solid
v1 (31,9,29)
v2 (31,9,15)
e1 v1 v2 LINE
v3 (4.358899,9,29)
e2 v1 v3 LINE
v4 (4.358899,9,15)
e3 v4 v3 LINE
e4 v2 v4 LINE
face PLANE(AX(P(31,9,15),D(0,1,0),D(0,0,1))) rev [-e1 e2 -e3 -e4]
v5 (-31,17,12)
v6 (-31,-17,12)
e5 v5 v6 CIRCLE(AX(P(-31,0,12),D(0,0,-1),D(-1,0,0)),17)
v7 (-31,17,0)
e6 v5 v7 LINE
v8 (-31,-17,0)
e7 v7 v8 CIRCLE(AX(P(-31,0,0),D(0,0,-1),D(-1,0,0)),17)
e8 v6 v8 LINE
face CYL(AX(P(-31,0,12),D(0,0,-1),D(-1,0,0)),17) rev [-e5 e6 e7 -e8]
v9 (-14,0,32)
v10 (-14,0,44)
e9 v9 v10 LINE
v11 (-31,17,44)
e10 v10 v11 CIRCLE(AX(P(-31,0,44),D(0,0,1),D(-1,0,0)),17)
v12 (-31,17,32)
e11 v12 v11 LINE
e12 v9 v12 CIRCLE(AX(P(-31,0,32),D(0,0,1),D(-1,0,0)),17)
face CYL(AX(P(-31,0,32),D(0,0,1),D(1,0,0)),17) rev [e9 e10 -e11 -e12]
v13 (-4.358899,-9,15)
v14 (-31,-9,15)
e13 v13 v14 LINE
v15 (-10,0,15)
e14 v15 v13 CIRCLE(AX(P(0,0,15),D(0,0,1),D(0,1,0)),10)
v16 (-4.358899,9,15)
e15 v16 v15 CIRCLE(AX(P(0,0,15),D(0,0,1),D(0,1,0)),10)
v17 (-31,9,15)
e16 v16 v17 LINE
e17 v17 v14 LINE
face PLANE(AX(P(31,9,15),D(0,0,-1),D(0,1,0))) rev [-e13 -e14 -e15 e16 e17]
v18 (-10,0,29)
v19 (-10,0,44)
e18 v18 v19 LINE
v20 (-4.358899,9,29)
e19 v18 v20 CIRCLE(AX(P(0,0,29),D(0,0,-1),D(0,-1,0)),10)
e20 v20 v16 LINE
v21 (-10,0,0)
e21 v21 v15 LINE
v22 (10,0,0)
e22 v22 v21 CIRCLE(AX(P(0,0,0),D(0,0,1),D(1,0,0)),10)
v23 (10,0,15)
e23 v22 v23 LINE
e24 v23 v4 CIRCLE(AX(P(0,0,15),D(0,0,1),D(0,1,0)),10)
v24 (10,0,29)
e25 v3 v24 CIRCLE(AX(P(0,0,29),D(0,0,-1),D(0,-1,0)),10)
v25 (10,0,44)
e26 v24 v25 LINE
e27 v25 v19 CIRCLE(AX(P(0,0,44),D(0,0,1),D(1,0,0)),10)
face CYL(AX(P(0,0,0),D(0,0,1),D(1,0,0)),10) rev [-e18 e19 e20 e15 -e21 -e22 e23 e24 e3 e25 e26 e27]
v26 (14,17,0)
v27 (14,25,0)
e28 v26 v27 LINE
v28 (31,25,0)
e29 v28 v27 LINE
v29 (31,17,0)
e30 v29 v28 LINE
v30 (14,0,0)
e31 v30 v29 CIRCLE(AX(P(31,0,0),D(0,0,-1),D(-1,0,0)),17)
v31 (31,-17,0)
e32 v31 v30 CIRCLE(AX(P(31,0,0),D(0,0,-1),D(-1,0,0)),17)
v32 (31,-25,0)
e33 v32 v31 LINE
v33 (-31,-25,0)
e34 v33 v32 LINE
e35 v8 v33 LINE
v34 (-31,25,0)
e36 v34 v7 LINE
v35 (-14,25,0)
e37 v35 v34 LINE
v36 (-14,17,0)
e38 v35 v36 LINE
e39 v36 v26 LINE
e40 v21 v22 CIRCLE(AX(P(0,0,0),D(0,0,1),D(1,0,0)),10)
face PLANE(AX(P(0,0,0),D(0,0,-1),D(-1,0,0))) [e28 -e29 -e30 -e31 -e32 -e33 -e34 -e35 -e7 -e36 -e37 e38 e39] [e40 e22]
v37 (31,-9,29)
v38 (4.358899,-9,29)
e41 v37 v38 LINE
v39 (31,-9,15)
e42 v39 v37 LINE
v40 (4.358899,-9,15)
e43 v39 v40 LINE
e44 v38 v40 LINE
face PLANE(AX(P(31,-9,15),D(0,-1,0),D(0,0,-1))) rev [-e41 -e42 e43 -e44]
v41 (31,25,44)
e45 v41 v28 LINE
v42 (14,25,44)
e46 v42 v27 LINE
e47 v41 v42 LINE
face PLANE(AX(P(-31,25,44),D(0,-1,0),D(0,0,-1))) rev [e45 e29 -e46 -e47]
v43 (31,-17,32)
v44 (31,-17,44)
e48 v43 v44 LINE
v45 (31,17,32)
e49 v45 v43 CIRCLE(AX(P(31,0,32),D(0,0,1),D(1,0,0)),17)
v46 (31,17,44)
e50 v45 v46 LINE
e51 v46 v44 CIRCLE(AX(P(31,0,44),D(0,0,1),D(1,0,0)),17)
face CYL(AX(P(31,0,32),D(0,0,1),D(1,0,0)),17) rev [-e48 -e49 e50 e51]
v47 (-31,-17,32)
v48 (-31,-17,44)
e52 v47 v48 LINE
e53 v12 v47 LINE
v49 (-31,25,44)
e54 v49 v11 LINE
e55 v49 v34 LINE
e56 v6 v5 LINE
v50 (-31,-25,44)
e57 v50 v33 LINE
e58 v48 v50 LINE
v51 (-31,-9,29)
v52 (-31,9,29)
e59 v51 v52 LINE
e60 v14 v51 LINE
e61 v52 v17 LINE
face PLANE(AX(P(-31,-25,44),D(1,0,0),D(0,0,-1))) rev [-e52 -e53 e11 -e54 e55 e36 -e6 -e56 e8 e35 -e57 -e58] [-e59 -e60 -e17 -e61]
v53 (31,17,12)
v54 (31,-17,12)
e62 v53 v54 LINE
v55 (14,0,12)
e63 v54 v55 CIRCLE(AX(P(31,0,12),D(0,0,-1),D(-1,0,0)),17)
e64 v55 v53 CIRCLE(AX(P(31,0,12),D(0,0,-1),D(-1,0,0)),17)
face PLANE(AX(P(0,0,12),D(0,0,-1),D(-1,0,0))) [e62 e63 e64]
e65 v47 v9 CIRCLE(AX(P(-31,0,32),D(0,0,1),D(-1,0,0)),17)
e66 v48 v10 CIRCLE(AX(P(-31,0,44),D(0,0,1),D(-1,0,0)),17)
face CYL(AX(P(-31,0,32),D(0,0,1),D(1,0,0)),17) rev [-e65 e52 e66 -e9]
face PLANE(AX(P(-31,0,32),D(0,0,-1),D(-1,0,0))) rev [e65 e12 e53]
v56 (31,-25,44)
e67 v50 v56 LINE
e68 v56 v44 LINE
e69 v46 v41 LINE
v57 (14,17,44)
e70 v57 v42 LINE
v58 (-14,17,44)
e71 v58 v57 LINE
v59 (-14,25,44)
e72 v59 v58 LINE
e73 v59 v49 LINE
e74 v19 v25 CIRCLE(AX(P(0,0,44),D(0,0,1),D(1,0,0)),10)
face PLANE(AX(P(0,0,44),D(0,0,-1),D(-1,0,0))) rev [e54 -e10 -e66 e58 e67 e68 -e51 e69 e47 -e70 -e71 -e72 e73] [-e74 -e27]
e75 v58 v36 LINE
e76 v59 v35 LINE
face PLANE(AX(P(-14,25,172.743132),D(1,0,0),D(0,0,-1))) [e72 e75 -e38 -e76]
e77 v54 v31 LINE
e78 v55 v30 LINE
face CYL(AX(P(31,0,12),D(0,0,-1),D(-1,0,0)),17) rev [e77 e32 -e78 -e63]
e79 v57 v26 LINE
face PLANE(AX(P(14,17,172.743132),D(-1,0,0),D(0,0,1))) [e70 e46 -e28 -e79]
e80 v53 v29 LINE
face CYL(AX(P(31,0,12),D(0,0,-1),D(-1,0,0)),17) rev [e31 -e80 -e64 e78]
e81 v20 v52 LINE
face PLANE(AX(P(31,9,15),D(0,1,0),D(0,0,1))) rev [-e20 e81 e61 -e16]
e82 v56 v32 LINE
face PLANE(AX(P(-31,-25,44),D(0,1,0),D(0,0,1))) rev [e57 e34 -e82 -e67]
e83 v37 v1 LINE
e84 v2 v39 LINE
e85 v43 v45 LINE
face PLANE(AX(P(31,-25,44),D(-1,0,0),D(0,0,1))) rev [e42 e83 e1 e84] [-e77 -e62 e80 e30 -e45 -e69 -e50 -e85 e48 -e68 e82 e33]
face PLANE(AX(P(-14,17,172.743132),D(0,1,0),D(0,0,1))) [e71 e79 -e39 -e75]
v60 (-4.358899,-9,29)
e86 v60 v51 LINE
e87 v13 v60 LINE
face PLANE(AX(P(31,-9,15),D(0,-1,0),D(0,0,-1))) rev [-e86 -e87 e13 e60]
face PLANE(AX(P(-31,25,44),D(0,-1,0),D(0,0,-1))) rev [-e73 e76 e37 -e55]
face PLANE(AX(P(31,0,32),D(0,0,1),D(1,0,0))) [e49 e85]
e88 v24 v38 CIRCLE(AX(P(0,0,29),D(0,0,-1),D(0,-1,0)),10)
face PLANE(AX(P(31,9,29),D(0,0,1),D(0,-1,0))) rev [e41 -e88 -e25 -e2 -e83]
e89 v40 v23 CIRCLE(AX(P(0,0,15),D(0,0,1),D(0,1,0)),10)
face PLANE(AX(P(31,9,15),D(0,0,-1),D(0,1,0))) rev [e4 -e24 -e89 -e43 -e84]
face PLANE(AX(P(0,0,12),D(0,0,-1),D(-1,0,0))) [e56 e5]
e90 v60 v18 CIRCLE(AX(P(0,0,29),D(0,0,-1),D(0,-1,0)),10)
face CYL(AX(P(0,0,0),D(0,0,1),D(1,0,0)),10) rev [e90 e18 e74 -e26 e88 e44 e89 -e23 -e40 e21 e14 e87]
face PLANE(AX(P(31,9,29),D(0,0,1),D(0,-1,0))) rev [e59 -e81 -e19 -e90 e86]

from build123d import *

# Parameters (mm, degrees)
BLOCK_PROFILE_SKETCH_W     = 62
BLOCK_PROFILE_SKETCH_H     = 50
BLOCK_62X50X44_DEPTH       = 44
THROUGH_HOLE_SKETCH_R      = 10
THROUGH_HOLE_20_DEPTH      = 44
TOP_SLOT_34X12_DEPTH       = 12
RELIEF_CUT_A_DEPTH         = 12
SIDE_RELIEF_CUT_DEPTH      = 60.3464405
SIDE_RELIEF_CUT_DEPTH_BACK = 60.3464405
RELIEF_START               = -12
RELIEF_CUT_B_DEPTH         = 12
RELIEF_CUT_C_DEPTH         = 12
WINDOW_SKETCH_W            = 14
WINDOW_SKETCH_H            = 18
WINDOW_CUT_DEPTH           = 81.031243899


with BuildPart() as part:
    # Block Profile Sketch → Block 62x50x44 (new body)
    with BuildSketch(Plane.XY):
        Rectangle(BLOCK_PROFILE_SKETCH_W, BLOCK_PROFILE_SKETCH_H)
    extrude(amount=BLOCK_62X50X44_DEPTH)

    # Through Hole Sketch → Through Hole Ø20 (cut)
    with BuildSketch(Plane.XY.offset(44)):
        Circle(THROUGH_HOLE_SKETCH_R)
    extrude(amount=-THROUGH_HOLE_20_DEPTH, mode=Mode.SUBTRACT)

    # Top Slot Sketch → Top Slot 34x12 (cut)
    with BuildSketch(Plane.XY.offset(44)):
        with BuildLine():
            Line((31, 17), (31, -17))
            ThreePointArc((31, -17), (14, 0), (31, 17))
        make_face()
    extrude(amount=-TOP_SLOT_34X12_DEPTH, mode=Mode.SUBTRACT)

    # Relief Cut A Sketch → Relief Cut A (cut)
    with BuildSketch(Plane.XY.offset(44)):
        with BuildLine():
            Line((31, -17), (31, 17))
            ThreePointArc((31, 17), (14, 0), (31, -17))
        make_face()
        with BuildLine():
            Line((-31, -17), (-31, 17))
            ThreePointArc((-31, 17), (-14, 0), (-31, -17))
        make_face()
    extrude(amount=-RELIEF_CUT_A_DEPTH, mode=Mode.SUBTRACT)

    # Side Relief Sketch → Side Relief Cut (cut, two sides: drawn at the far end of the back side and taken through both)
    with BuildSketch(Plane.XY.offset(44).offset(-SIDE_RELIEF_CUT_DEPTH_BACK)):
        Polygon((-14, 169.536240471), (-14, 25), (-14, 17), (14, 17), (14, 25), (14, 169.536240471), (14, 458.608721412), (-14, 458.608721412), align=None)
    extrude(amount=SIDE_RELIEF_CUT_DEPTH + SIDE_RELIEF_CUT_DEPTH_BACK, mode=Mode.SUBTRACT)

    # Relief Cut B Sketch → Relief Cut B (cut)
    with BuildSketch(Plane(origin=(0, 0, 0), x_dir=(-1, 0, 0), z_dir=(0, 0, -1)).offset(RELIEF_START)):
        with BuildLine():
            ThreePointArc((31, 17), (14, 0), (31, -17))
            Line((31, -17), (31, 17))
        make_face()
    extrude(amount=RELIEF_CUT_B_DEPTH, mode=Mode.SUBTRACT)

    # Relief Cut C Sketch → Relief Cut C (cut)
    with BuildSketch(Plane(origin=(0, 0, 0), x_dir=(-1, 0, 0), z_dir=(0, 0, -1)).offset(RELIEF_START)):
        with BuildLine():
            ThreePointArc((-31, -17), (-14, 0), (-31, 17))
            Line((-31, 17), (-31, -17))
        make_face()
    extrude(amount=RELIEF_CUT_C_DEPTH, mode=Mode.SUBTRACT)

    # Window Sketch → Window Cut (cut, through all)
    with BuildSketch(Plane.ZY.offset(31)):
        with Locations((22, 0)):
            Rectangle(WINDOW_SKETCH_W, WINDOW_SKETCH_H)
    extrude(amount=-WINDOW_CUT_DEPTH, mode=Mode.SUBTRACT)


solid = part.part
